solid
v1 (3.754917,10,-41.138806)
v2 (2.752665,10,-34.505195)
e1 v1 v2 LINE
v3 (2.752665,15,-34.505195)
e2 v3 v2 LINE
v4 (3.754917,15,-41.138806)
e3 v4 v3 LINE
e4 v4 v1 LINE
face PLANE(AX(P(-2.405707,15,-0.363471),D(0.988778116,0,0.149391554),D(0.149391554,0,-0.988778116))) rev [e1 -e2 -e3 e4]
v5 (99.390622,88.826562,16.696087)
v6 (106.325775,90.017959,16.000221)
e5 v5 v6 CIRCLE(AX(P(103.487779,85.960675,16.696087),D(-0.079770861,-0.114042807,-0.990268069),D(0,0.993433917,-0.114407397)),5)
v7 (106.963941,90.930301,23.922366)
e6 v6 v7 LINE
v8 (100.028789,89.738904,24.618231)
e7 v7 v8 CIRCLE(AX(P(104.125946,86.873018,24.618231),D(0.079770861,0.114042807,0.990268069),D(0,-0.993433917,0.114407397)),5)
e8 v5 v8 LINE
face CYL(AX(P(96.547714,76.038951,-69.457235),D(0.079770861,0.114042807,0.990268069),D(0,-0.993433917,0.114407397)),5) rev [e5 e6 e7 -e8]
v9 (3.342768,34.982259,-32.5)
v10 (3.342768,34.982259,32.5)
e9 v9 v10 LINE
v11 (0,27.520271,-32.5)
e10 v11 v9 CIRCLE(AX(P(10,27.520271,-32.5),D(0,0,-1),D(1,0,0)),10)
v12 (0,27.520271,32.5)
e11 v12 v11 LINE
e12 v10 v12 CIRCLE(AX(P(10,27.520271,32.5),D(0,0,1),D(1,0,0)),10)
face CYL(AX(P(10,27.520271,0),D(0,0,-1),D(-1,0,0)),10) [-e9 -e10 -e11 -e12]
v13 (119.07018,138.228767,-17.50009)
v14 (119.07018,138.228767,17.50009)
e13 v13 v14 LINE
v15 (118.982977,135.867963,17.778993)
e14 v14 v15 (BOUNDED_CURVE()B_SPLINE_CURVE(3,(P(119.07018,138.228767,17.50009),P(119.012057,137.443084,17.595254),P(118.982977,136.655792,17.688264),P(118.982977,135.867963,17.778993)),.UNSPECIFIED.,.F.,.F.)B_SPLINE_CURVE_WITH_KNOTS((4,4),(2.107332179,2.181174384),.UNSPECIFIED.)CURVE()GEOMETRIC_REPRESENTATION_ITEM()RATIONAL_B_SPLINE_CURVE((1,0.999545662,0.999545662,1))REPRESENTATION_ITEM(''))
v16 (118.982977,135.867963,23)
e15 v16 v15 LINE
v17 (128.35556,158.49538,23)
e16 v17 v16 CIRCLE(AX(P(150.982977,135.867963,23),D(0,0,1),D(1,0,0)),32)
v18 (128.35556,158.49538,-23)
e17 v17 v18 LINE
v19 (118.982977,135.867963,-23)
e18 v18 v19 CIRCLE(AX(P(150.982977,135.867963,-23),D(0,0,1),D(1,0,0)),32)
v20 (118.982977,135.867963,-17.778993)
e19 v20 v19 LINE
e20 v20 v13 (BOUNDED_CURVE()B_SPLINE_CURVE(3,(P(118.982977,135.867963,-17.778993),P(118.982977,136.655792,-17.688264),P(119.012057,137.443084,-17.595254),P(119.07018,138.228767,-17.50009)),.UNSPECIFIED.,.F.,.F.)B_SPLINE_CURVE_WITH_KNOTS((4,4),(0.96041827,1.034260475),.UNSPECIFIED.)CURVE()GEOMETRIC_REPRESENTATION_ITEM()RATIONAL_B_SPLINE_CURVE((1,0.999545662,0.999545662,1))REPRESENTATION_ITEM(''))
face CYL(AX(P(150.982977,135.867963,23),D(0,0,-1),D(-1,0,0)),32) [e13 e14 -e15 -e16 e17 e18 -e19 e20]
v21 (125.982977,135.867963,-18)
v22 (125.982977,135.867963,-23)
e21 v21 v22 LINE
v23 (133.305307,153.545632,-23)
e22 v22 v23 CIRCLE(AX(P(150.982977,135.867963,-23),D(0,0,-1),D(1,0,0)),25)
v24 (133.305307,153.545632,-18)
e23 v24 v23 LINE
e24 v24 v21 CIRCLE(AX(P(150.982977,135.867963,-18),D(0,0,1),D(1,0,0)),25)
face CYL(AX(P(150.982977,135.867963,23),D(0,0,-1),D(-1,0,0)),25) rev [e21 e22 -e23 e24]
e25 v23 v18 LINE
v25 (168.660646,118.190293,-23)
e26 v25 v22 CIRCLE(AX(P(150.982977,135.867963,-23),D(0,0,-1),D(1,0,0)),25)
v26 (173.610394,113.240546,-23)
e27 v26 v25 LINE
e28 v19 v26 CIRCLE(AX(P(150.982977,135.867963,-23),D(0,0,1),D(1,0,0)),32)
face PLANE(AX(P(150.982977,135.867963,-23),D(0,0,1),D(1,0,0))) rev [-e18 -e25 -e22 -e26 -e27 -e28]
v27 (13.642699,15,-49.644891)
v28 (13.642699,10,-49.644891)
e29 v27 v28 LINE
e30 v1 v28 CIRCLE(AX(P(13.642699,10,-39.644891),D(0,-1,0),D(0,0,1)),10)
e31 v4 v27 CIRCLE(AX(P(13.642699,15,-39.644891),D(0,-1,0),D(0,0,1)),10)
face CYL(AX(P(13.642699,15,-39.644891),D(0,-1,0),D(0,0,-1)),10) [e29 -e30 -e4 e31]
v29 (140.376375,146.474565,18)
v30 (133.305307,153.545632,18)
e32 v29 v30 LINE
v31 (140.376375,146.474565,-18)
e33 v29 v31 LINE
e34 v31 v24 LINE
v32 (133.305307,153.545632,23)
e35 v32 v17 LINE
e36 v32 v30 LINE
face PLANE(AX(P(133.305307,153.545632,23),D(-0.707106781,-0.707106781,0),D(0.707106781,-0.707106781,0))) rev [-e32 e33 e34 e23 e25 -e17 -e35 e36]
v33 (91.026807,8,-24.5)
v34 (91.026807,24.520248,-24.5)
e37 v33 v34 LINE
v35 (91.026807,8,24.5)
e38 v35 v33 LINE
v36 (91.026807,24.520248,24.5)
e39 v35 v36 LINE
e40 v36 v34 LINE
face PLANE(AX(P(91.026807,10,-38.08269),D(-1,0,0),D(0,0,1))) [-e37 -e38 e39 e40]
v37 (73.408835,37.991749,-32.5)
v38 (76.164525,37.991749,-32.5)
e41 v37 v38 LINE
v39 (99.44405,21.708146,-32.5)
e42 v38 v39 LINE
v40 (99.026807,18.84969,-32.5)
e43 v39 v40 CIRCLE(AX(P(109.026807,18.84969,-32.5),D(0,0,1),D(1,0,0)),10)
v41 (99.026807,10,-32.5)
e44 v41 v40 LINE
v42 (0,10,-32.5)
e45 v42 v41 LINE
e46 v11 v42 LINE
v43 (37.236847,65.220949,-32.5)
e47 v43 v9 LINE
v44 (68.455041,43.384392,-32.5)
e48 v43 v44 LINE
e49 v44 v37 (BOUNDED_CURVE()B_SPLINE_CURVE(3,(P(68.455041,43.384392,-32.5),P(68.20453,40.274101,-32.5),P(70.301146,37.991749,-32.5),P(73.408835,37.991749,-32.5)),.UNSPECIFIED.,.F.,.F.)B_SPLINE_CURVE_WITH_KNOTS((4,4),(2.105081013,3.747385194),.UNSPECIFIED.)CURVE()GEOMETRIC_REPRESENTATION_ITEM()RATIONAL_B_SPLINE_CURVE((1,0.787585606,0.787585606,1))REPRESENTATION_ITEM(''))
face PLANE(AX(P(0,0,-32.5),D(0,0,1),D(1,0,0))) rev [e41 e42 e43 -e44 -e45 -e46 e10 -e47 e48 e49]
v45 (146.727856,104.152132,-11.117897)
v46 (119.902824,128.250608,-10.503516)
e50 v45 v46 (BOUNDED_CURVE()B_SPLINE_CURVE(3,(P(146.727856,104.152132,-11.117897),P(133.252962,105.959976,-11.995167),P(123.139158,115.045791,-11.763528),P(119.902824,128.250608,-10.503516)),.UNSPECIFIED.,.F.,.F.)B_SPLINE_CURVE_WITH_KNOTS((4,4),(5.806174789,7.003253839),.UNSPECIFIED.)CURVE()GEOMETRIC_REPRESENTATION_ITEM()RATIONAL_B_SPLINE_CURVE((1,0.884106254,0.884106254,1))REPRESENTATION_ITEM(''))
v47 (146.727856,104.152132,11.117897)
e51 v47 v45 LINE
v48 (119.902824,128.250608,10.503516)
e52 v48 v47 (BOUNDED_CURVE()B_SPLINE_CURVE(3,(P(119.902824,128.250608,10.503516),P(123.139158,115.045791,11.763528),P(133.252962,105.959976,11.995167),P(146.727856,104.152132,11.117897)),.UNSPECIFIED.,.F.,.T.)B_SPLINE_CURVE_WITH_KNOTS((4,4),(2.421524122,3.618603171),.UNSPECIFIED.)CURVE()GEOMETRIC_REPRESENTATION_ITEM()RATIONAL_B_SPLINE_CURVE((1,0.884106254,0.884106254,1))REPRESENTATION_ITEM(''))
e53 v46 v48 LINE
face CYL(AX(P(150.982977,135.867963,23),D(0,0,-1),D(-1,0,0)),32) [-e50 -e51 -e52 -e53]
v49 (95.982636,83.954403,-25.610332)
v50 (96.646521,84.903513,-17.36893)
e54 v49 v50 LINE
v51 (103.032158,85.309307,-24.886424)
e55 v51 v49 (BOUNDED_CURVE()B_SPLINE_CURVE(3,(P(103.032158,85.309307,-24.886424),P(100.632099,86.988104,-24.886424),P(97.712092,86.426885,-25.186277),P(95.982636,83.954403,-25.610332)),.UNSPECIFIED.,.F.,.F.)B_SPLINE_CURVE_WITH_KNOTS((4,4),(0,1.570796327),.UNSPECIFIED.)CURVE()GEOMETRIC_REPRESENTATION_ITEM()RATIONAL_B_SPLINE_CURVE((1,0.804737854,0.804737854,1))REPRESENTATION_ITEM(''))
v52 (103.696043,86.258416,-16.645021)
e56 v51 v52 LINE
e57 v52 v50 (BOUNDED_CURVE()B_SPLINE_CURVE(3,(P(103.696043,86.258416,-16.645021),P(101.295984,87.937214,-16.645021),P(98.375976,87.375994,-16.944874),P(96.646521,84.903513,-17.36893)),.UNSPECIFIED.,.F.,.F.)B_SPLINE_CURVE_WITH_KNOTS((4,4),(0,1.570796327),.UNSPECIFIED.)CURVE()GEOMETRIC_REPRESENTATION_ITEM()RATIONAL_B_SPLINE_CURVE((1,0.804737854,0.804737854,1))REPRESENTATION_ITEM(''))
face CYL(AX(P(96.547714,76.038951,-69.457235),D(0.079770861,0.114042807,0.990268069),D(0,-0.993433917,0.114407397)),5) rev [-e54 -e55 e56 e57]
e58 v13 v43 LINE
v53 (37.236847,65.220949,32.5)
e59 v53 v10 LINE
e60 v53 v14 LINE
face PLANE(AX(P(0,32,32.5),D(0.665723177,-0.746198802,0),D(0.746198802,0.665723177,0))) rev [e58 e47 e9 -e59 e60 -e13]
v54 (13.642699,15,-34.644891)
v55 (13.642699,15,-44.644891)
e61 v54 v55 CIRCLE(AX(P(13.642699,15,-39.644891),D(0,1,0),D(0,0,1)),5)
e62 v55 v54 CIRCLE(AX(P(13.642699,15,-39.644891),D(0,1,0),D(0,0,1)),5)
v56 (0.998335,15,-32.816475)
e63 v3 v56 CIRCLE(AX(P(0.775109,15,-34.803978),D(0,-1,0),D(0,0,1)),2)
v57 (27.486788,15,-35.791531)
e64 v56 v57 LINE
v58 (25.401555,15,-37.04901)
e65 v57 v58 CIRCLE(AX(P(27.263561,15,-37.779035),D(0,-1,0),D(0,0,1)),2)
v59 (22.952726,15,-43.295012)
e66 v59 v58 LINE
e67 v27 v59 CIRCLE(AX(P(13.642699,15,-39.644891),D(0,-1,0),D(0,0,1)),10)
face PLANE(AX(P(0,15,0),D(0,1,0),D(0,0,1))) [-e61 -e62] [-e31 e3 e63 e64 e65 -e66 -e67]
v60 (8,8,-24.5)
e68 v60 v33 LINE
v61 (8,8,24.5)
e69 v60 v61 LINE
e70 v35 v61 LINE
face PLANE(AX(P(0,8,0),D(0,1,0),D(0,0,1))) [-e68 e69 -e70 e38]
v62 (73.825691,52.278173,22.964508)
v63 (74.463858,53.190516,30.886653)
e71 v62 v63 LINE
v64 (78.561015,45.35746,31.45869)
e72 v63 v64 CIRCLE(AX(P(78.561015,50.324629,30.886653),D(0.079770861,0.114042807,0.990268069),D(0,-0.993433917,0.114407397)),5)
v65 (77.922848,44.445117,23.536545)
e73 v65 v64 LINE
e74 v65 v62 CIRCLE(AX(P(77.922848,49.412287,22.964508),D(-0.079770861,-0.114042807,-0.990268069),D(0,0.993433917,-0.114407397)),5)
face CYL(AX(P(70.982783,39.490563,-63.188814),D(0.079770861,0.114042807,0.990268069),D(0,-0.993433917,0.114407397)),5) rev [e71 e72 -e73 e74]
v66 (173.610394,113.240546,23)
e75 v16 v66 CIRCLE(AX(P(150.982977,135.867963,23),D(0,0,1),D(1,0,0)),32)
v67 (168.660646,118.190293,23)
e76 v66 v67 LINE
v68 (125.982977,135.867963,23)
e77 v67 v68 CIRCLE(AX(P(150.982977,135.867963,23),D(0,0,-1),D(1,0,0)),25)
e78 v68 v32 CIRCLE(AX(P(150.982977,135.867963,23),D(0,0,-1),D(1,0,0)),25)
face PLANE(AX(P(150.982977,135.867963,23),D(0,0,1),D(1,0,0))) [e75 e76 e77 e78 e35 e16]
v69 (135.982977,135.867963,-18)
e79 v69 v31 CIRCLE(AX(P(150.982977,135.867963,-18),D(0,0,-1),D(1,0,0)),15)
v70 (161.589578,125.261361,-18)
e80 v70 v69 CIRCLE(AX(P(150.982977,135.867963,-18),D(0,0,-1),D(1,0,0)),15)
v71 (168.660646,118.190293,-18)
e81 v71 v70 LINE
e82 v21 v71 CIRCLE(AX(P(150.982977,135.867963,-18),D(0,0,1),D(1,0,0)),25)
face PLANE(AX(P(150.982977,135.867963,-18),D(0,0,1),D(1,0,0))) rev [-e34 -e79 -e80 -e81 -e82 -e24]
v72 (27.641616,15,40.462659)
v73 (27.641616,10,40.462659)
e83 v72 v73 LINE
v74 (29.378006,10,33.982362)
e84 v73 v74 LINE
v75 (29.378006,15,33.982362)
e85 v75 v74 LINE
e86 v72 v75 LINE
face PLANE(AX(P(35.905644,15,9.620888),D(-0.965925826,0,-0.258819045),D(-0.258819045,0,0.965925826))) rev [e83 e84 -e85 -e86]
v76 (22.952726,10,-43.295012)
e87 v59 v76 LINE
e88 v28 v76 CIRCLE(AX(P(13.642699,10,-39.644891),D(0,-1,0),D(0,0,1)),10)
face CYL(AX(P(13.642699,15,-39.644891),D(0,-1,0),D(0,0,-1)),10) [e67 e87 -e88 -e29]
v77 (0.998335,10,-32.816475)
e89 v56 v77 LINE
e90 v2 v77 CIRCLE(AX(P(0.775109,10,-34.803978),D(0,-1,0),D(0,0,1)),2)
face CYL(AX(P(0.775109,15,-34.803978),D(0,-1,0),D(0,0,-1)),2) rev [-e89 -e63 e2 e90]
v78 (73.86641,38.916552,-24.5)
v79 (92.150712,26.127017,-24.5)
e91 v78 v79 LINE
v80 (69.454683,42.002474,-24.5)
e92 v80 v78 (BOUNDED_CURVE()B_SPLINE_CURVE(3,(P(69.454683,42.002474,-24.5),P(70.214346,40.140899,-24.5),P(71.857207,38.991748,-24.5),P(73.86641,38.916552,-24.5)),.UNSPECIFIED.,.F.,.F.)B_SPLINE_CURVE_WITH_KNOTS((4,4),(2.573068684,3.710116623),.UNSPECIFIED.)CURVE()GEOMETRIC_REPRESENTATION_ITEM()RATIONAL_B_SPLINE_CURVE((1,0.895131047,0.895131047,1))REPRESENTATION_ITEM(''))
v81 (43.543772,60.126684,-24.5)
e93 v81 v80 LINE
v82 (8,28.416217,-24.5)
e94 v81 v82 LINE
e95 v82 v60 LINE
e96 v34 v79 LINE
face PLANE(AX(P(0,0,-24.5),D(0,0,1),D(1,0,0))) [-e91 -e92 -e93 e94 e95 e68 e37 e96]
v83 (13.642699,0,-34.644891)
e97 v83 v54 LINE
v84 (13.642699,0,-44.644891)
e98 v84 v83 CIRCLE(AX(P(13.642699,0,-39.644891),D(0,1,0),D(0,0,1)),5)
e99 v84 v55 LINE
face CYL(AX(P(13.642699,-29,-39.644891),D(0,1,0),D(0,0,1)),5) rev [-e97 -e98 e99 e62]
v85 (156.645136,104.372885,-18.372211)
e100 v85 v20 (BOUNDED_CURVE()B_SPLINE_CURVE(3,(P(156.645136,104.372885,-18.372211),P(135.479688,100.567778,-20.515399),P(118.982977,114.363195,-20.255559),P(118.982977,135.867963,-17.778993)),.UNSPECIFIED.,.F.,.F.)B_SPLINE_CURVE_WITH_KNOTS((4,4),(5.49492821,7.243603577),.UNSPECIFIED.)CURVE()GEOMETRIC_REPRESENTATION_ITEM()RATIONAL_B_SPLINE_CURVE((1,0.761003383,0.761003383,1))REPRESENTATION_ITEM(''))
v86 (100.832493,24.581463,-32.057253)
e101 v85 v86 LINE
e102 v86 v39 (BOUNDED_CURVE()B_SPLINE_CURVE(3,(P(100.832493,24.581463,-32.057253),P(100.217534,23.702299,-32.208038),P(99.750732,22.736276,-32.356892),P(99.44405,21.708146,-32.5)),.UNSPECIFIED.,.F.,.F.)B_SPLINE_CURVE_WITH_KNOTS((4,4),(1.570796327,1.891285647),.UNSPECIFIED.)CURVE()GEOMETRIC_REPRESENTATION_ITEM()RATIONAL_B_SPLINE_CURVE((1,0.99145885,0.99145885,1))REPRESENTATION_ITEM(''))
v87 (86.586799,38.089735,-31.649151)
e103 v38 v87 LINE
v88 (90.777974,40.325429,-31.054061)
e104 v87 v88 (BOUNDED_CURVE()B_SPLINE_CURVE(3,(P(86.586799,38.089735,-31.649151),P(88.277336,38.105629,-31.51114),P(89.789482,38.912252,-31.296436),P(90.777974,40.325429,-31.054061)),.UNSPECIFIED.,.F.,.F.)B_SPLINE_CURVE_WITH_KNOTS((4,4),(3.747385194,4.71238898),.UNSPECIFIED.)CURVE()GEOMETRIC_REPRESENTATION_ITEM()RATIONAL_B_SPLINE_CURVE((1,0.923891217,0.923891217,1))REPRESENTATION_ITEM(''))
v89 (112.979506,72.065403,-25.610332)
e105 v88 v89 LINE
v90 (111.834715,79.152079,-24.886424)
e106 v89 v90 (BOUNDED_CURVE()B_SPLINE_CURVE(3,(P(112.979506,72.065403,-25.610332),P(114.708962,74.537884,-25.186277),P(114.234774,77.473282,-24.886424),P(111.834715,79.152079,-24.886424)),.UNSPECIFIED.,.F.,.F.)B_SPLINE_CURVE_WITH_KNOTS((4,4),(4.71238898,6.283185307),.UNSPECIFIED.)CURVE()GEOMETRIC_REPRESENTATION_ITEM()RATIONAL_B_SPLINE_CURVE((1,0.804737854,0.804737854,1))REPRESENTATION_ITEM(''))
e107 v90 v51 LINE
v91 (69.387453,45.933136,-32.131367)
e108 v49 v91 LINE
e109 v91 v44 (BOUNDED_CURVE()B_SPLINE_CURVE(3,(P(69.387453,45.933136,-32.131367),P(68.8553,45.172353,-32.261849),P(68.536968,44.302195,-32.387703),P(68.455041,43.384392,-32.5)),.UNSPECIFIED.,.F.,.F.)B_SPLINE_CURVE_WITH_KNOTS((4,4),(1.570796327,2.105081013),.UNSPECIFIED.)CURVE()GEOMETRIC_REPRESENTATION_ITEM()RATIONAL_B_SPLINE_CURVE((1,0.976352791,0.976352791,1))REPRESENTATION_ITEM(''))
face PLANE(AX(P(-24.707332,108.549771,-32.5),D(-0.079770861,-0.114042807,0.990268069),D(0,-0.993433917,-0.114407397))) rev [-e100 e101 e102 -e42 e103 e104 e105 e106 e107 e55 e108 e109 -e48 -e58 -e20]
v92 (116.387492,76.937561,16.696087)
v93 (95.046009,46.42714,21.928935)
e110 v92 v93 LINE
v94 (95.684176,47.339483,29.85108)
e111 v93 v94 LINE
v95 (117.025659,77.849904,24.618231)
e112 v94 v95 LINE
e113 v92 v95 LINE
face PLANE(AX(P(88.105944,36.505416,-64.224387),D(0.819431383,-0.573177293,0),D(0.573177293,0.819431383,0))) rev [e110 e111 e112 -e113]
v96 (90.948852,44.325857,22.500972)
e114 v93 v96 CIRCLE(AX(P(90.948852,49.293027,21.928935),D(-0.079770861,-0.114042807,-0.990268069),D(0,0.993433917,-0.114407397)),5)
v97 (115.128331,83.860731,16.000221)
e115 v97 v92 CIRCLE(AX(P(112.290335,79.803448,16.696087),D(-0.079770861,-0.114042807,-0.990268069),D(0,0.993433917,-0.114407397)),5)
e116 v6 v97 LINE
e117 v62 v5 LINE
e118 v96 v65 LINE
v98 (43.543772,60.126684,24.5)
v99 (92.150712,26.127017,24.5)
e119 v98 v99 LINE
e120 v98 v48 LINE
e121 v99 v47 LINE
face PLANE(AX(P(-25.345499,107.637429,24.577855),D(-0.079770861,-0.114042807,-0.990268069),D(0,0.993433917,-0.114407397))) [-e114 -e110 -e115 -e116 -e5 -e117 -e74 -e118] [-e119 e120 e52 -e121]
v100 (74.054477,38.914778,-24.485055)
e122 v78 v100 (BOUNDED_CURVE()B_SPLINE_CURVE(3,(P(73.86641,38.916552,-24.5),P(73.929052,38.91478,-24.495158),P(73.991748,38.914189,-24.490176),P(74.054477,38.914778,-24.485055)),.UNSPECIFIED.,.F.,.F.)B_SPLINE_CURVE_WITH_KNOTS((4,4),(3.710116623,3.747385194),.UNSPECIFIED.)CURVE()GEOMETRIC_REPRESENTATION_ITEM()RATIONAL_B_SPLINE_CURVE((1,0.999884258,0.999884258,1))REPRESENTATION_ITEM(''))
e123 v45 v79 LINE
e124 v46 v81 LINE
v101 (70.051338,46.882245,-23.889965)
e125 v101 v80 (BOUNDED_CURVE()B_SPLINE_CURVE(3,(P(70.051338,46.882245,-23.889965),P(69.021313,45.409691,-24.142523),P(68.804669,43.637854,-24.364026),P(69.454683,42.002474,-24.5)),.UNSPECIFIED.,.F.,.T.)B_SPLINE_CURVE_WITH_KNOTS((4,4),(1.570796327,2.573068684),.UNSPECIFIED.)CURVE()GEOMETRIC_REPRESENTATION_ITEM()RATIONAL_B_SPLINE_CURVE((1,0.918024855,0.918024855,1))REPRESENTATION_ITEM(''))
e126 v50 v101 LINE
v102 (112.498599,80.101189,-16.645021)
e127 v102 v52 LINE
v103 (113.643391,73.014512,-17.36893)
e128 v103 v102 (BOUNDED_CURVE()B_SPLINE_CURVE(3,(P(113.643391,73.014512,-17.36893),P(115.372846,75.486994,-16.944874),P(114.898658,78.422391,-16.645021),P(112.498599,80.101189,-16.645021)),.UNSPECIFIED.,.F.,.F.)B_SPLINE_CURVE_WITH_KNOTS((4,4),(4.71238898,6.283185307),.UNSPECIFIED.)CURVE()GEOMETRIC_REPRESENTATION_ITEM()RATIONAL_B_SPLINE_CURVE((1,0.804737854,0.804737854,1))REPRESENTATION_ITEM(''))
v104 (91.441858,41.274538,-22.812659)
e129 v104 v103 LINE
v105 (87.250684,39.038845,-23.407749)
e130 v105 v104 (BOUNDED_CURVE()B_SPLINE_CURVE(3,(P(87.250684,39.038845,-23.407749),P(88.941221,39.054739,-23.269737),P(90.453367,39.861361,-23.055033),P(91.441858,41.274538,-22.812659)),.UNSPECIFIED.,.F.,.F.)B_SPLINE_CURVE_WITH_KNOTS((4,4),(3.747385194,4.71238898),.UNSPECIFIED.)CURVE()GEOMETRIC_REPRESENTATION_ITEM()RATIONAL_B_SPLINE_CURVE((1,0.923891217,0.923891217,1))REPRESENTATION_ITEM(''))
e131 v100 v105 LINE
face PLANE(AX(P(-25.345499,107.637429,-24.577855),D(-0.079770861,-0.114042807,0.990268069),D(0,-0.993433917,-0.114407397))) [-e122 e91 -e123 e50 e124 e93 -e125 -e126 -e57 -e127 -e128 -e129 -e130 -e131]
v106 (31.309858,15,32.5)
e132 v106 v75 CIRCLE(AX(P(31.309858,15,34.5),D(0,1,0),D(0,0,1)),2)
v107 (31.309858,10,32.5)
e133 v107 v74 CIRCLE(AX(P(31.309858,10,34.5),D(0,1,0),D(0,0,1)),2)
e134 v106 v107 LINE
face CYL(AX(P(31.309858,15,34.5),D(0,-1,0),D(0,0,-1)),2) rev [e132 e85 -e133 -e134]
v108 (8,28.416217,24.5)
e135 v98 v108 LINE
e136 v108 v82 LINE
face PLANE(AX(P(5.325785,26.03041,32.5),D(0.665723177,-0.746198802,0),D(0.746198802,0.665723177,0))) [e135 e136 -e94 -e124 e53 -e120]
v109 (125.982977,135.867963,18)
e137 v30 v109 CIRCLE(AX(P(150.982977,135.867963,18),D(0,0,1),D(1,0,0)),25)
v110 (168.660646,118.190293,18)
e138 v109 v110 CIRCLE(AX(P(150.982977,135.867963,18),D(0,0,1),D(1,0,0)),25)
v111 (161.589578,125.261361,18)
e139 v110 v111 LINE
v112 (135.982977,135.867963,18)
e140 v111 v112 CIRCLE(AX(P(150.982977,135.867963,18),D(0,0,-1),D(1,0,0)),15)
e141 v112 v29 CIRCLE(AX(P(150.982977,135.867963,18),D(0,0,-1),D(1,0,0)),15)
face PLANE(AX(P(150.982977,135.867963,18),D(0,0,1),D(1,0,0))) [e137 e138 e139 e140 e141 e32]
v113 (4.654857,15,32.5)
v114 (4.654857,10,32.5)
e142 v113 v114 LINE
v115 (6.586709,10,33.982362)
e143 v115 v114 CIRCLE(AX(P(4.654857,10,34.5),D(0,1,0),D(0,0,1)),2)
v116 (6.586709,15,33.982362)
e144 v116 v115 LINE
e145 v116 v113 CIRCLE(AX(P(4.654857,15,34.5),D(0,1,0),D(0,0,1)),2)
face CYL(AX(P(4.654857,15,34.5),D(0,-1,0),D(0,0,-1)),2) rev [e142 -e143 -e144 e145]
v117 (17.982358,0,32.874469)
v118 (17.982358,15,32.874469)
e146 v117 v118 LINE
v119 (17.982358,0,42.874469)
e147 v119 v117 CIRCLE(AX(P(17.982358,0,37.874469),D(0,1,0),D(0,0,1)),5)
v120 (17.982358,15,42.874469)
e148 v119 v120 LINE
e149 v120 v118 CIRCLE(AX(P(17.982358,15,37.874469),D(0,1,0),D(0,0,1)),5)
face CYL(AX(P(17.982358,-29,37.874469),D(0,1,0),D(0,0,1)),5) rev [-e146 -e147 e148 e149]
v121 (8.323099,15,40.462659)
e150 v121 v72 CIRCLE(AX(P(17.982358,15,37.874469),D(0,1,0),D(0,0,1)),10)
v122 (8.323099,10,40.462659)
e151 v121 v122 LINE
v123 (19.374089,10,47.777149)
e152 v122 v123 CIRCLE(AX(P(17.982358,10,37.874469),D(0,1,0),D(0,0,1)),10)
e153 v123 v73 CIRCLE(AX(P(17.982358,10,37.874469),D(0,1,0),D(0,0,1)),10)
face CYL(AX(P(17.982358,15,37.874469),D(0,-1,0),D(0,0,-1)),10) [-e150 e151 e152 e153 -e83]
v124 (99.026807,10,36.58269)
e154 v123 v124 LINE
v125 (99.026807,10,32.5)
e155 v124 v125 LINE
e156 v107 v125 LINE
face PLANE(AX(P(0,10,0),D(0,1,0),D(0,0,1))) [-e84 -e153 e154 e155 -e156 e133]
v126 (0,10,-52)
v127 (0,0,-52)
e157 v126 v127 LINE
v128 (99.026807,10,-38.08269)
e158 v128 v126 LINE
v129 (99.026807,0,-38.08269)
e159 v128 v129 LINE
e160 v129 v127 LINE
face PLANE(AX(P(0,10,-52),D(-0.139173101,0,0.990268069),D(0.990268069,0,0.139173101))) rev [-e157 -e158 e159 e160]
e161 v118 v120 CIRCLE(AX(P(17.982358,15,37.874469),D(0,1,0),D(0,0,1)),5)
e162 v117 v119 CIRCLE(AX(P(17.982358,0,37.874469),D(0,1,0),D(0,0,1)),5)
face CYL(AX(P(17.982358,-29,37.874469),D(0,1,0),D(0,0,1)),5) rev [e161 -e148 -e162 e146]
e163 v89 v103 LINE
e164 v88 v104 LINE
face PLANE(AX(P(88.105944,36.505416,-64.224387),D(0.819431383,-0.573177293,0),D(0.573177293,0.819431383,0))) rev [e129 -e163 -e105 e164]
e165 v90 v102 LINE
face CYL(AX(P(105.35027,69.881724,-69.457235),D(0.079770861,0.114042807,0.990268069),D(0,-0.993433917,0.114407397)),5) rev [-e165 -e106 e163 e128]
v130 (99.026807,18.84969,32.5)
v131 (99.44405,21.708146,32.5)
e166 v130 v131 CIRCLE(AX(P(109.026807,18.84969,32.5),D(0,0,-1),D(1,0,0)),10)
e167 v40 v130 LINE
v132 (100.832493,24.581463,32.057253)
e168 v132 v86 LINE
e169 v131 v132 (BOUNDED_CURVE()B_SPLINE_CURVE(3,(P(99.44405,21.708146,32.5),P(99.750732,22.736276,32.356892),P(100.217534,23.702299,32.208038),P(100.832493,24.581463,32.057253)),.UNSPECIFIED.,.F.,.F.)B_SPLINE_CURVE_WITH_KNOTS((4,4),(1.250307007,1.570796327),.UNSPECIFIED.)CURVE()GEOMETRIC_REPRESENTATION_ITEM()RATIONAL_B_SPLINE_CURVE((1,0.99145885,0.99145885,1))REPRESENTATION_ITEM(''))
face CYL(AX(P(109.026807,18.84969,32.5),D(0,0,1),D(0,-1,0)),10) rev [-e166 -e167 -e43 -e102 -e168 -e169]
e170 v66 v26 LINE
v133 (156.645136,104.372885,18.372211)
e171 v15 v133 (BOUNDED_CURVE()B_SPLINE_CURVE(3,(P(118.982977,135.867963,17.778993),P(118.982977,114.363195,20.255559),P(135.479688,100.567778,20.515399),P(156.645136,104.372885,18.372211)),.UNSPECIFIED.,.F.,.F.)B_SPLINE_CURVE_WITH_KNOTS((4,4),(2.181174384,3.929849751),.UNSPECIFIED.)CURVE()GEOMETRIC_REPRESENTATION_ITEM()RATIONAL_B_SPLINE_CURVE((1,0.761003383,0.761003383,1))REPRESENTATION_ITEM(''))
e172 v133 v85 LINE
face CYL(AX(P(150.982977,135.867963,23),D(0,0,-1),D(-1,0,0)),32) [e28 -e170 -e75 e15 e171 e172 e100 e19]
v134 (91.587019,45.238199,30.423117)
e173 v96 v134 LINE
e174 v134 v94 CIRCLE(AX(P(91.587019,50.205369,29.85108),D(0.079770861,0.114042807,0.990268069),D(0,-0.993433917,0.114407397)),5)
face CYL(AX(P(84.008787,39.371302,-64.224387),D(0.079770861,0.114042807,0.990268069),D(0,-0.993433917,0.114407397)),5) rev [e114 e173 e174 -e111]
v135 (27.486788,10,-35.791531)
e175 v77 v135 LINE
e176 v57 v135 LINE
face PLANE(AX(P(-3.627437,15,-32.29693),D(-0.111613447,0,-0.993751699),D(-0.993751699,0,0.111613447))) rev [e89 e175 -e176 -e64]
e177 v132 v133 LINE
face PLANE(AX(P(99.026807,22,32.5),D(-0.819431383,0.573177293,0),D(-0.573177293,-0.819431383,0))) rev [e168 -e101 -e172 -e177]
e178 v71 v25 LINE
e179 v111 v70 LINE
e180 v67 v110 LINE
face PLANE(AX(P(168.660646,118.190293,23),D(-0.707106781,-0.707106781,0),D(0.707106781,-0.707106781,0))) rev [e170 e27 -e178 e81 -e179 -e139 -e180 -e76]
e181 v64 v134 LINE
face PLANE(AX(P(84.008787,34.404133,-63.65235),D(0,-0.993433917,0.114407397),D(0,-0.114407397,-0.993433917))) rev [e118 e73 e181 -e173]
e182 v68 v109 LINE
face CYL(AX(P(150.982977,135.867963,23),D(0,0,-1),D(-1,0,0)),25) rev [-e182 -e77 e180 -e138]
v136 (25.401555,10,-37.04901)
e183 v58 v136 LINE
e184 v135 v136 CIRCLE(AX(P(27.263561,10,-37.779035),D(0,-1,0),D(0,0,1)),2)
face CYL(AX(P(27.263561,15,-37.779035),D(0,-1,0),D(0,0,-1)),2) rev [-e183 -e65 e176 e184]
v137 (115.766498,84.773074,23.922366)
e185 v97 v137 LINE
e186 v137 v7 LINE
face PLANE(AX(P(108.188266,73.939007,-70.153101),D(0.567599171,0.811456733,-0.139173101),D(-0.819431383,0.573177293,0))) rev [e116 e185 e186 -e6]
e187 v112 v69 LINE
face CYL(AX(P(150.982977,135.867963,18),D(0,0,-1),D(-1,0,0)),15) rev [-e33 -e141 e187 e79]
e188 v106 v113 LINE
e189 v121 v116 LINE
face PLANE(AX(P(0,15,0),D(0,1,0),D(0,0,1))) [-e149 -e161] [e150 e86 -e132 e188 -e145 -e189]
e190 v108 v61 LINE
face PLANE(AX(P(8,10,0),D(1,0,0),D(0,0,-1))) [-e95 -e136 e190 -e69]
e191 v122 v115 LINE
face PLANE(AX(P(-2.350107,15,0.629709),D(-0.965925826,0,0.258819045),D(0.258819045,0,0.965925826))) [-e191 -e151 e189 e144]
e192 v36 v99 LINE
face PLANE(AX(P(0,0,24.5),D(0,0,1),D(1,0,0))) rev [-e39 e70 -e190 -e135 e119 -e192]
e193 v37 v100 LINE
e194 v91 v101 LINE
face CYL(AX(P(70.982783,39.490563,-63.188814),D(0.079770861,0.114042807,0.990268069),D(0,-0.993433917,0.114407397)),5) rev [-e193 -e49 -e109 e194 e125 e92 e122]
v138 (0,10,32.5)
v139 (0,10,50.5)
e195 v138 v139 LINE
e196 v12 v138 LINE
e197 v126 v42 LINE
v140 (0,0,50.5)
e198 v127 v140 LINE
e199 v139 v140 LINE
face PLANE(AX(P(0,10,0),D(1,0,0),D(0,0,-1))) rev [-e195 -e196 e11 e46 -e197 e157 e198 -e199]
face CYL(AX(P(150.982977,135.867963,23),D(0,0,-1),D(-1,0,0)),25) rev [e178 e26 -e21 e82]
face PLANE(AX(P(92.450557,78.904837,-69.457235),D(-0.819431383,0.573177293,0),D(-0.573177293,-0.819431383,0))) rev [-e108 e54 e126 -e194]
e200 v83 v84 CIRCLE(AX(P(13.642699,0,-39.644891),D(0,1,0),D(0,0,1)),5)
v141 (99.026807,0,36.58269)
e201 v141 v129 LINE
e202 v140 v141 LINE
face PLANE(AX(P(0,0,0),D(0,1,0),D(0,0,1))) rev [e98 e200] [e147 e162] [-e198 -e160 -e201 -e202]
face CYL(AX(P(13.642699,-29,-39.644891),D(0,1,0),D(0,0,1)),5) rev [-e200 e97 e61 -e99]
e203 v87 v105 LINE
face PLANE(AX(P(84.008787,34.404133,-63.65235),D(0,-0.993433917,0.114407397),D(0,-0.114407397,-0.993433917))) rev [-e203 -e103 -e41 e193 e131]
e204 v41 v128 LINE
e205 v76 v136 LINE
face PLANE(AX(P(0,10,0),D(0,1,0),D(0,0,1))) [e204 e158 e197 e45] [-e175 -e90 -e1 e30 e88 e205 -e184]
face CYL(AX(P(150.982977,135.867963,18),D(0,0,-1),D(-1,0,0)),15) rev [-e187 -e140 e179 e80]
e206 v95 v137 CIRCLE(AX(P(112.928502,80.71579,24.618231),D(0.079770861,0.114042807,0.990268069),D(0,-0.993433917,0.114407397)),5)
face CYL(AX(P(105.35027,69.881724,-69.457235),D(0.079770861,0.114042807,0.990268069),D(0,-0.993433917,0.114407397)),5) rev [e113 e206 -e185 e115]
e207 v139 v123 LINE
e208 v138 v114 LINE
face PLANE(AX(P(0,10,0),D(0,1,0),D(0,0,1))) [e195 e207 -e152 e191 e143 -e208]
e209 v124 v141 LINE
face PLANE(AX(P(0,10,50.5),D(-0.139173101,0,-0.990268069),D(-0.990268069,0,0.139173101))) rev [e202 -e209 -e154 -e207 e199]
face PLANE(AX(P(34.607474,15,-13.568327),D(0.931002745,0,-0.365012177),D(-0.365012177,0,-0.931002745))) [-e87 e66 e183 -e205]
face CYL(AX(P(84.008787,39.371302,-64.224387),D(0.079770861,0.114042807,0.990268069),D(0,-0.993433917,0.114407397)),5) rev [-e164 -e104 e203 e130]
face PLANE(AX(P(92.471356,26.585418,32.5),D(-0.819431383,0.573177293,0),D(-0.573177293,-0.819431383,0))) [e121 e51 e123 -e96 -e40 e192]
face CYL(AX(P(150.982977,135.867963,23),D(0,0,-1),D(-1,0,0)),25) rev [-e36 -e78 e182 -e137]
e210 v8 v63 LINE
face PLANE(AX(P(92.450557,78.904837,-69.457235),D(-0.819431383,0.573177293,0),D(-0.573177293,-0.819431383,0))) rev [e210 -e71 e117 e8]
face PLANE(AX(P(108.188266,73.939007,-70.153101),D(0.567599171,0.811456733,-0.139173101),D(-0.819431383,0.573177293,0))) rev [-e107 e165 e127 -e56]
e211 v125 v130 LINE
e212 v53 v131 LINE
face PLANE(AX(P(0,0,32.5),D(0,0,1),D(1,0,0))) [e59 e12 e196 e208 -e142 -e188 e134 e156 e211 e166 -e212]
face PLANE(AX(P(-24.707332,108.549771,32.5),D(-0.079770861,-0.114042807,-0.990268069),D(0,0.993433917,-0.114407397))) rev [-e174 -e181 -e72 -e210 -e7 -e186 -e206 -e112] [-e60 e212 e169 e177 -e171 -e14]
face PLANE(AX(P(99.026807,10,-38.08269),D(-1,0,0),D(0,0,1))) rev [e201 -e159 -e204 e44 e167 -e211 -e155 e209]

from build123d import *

# Parameters (mm, degrees)
BASE_PLATE_10MM_DEPTH    = 10
INCLINED_BODY_DEPTH      = 32.5
INCLINE_TRIM_CUT_DEPTH   = 151
BODY_SHELL_8MM_T         = -8
PIPE_COLLAR_DEPTH        = 23
COLLAR_BORE_SKETCH_R     = 25
COLLAR_BORE_CUT_DEPTH    = 46
COLLAR_FLANGE_DEPTH      = 18
SIDE_SLOT_CUT_DEPTH      = 95
MOUNTING_LUG_DEPTH       = 5
LUG_HOLE_SKETCH_R        = 5
LUG_HOLE_CUT_DEPTH       = 44
BODY_EDGE_FILLET_R10_A_R = 10
BODY_EDGE_FILLET_R10_B_R = 10


with BuildPart() as part:
    # Base Plate Sketch → Base Plate 10mm (new body)
    with BuildSketch(Plane(origin=(0, 0, 0), x_dir=(1, 0, 0), z_dir=(0, 1, 0))):
        Polygon((0, 0), (0, 52), (99.026806874, 38.082689904), (99.026806874, -36.582689904), (0, -50.5), align=None)
    extrude(amount=BASE_PLATE_10MM_DEPTH)

    # Inclined Body Sketch → Inclined Body (add, symmetric)
    with BuildSketch(Plane.XY):
        Polygon((0, 10), (0, 32), (134.688366927, 152.162572436), (167.277586184, 119.573353179), (99.026806874, 22), (99.026806874, 10), align=None)
    extrude(amount=INCLINED_BODY_DEPTH, both=True)

    # Incline Trim Sketch → Incline Trim Cut (cut)
    with BuildSketch(Plane(origin=(56.160363076, -39.283148743, 0), x_dir=(0, 0, -1), z_dir=(0.8194313825543525, -0.5731772930647745, 0))):
        Polygon((32.5, 74.787407521), (5.510372788, 266.828583807), (32.5, 266.828583807), (32.5, 193.861872152), align=None)
        Polygon((-32.5, 74.787407521), (-5.510372788, 266.828583807), (-32.5, 266.828583807), (-32.5, 193.861872152), align=None)
    extrude(amount=-INCLINE_TRIM_CUT_DEPTH, mode=Mode.SUBTRACT)

    # Body Shell 8mm
    body_shell_8mm_openings = [part.faces().sort_by_distance(p)[0] for p in [
        (151.184475908, 135.666463456, 0),
    ]]
    offset(amount=BODY_SHELL_8MM_T, openings=body_shell_8mm_openings, kind=Kind.INTERSECTION)

    # Pipe Collar Sketch → Pipe Collar (add, symmetric)
    with BuildSketch(Plane.XY):
        with BuildLine():
            Line((168.660646085, 118.190293278), (173.610393554, 113.24054581))
            ThreePointArc((173.610393554, 113.24054581), (128.355559558, 113.24054581), (128.355559558, 158.495379806))
            Line((128.355559558, 158.495379806), (133.305307026, 153.545632337))
            ThreePointArc((133.305307026, 153.545632337), (133.305307026, 118.190293278), (168.660646085, 118.190293278))
        make_face()
    extrude(amount=PIPE_COLLAR_DEPTH, both=True)

    # Collar Bore Sketch → Collar Bore Cut (cut)
    with BuildSketch(Plane.XY.offset(23)):
        with Locations((150.982976556, 135.867962808)):
            Circle(COLLAR_BORE_SKETCH_R)
    extrude(amount=-COLLAR_BORE_CUT_DEPTH, mode=Mode.SUBTRACT)

    # Collar Flange Sketch → Collar Flange (add, symmetric)
    with BuildSketch(Plane.XY):
        with BuildLine():
            Line((133.305307026, 153.545632337), (140.376374838, 146.474564526))
            ThreePointArc((140.376374838, 146.474564526), (140.376374838, 125.26136109), (161.589578273, 125.26136109))
            Line((161.589578273, 125.26136109), (168.660646085, 118.190293278))
            ThreePointArc((168.660646085, 118.190293278), (133.305307026, 118.190293278), (133.305307026, 153.545632337))
        make_face()
    extrude(amount=COLLAR_FLANGE_DEPTH, both=True)

    # Side Slot Sketch → Side Slot Cut (cut)
    with BuildSketch(Plane(origin=(3.397609111, 4.857323493, 42.177604188), x_dir=(0.9968132270848588, -0.009126376589251743, -0.07924707918290198), z_dir=(0.07977086127571884, 0.11404280653407992, 0.9902680687415709))):
        with BuildLine():
            Line((92.581603623, 43.613463299), (113.99131411, 74.522227016))
            ThreePointArc((113.99131411, 74.522227016), (114.800629853, 78.262503606), (112.728127564, 81.479551196))
            Line((112.728127564, 81.479551196), (103.897429804, 87.596349789))
            ThreePointArc((103.897429804, 87.596349789), (100.157153215, 88.405665533), (96.940105624, 86.333163243))
            Line((96.940105624, 86.333163243), (71.29344512, 49.307600933))
            ThreePointArc((71.29344512, 49.307600933), (70.974516355, 44.140547642), (75.403700483, 41.460532116))
            Line((75.403700483, 41.460532116), (88.47134826, 41.460532116))
            ThreePointArc((88.47134826, 41.460532116), (90.791332734, 42.031347987), (92.581603623, 43.613463299))
        make_face()
    extrude(amount=-SIDE_SLOT_CUT_DEPTH, mode=Mode.SUBTRACT)

    # Mounting Lug Sketch → Mounting Lug (add)
    with BuildSketch(Plane(origin=(0, 10, 0), x_dir=(1, 0, 0), z_dir=(0, 1, 0))):
        with BuildLine():
            ThreePointArc((3.754917352, 41.138806093), (12.526564043, 49.582407535), (22.952725963, 43.29501232))
            Line((22.952725963, 43.29501232), (25.401555204, 37.04901044))
            ThreePointArc((25.401555204, 37.04901044), (26.230743087, 36.066350412), (27.486787588, 35.791531397))
            Line((27.486787588, 35.791531397), (0.998335406, 32.816474884))
            ThreePointArc((0.998335406, 32.816474884), (2.162121722, 33.363077745), (2.752664744, 34.505195172))
            Line((2.752664744, 34.505195172), (3.754917352, 41.138806093))
        make_face()
        with BuildLine():
            Line((31.309858058, -32.5), (4.654857397, -32.5))
            ThreePointArc((4.654857397, -32.5), (5.872380255, -32.913293319), (6.58670905, -33.98236191))
            Line((6.58670905, -33.98236191), (8.323099465, -40.462659161))
            ThreePointArc((8.323099465, -40.462659161), (12.462987997, -46.213327011), (19.374089028, -47.777149356))
            ThreePointArc((19.374089028, -47.777149356), (24.60855832, -45.364025821), (27.641615991, -40.462659161))
            Line((27.641615991, -40.462659161), (29.378006406, -33.98236191))
            ThreePointArc((29.378006406, -33.98236191), (30.0923352, -32.913293319), (31.309858058, -32.5))
        make_face()
    extrude(amount=MOUNTING_LUG_DEPTH)

    # Lug Hole Sketch → Lug Hole Cut (cut)
    with BuildSketch(Plane(origin=(0, 15, 0), x_dir=(1, 0, 0), z_dir=(0, 1, 0))):
        with Locations(Location((13.642698516, 39.64489055, 0), (0, 0, 270))):
            Circle(LUG_HOLE_SKETCH_R)
        with Locations(Location((17.982357728, -37.87446871, 0), (0, 0, 270))):
            Circle(LUG_HOLE_SKETCH_R)
    extrude(amount=-LUG_HOLE_CUT_DEPTH, mode=Mode.SUBTRACT)

    # Body Edge Fillet R10 A
    body_edge_fillet_r10_a_edges = [part.edges().sort_by_distance(p)[0] for p in [
        (0, 32, 0),
    ]]
    fillet(body_edge_fillet_r10_a_edges, radius=BODY_EDGE_FILLET_R10_A_R)

    # Body Edge Fillet R10 B
    body_edge_fillet_r10_b_edges = [part.edges().sort_by_distance(p)[0] for p in [
        (99.026806874, 22, 0),
    ]]
    fillet(body_edge_fillet_r10_b_edges, radius=BODY_EDGE_FILLET_R10_B_R)


solid = part.part
